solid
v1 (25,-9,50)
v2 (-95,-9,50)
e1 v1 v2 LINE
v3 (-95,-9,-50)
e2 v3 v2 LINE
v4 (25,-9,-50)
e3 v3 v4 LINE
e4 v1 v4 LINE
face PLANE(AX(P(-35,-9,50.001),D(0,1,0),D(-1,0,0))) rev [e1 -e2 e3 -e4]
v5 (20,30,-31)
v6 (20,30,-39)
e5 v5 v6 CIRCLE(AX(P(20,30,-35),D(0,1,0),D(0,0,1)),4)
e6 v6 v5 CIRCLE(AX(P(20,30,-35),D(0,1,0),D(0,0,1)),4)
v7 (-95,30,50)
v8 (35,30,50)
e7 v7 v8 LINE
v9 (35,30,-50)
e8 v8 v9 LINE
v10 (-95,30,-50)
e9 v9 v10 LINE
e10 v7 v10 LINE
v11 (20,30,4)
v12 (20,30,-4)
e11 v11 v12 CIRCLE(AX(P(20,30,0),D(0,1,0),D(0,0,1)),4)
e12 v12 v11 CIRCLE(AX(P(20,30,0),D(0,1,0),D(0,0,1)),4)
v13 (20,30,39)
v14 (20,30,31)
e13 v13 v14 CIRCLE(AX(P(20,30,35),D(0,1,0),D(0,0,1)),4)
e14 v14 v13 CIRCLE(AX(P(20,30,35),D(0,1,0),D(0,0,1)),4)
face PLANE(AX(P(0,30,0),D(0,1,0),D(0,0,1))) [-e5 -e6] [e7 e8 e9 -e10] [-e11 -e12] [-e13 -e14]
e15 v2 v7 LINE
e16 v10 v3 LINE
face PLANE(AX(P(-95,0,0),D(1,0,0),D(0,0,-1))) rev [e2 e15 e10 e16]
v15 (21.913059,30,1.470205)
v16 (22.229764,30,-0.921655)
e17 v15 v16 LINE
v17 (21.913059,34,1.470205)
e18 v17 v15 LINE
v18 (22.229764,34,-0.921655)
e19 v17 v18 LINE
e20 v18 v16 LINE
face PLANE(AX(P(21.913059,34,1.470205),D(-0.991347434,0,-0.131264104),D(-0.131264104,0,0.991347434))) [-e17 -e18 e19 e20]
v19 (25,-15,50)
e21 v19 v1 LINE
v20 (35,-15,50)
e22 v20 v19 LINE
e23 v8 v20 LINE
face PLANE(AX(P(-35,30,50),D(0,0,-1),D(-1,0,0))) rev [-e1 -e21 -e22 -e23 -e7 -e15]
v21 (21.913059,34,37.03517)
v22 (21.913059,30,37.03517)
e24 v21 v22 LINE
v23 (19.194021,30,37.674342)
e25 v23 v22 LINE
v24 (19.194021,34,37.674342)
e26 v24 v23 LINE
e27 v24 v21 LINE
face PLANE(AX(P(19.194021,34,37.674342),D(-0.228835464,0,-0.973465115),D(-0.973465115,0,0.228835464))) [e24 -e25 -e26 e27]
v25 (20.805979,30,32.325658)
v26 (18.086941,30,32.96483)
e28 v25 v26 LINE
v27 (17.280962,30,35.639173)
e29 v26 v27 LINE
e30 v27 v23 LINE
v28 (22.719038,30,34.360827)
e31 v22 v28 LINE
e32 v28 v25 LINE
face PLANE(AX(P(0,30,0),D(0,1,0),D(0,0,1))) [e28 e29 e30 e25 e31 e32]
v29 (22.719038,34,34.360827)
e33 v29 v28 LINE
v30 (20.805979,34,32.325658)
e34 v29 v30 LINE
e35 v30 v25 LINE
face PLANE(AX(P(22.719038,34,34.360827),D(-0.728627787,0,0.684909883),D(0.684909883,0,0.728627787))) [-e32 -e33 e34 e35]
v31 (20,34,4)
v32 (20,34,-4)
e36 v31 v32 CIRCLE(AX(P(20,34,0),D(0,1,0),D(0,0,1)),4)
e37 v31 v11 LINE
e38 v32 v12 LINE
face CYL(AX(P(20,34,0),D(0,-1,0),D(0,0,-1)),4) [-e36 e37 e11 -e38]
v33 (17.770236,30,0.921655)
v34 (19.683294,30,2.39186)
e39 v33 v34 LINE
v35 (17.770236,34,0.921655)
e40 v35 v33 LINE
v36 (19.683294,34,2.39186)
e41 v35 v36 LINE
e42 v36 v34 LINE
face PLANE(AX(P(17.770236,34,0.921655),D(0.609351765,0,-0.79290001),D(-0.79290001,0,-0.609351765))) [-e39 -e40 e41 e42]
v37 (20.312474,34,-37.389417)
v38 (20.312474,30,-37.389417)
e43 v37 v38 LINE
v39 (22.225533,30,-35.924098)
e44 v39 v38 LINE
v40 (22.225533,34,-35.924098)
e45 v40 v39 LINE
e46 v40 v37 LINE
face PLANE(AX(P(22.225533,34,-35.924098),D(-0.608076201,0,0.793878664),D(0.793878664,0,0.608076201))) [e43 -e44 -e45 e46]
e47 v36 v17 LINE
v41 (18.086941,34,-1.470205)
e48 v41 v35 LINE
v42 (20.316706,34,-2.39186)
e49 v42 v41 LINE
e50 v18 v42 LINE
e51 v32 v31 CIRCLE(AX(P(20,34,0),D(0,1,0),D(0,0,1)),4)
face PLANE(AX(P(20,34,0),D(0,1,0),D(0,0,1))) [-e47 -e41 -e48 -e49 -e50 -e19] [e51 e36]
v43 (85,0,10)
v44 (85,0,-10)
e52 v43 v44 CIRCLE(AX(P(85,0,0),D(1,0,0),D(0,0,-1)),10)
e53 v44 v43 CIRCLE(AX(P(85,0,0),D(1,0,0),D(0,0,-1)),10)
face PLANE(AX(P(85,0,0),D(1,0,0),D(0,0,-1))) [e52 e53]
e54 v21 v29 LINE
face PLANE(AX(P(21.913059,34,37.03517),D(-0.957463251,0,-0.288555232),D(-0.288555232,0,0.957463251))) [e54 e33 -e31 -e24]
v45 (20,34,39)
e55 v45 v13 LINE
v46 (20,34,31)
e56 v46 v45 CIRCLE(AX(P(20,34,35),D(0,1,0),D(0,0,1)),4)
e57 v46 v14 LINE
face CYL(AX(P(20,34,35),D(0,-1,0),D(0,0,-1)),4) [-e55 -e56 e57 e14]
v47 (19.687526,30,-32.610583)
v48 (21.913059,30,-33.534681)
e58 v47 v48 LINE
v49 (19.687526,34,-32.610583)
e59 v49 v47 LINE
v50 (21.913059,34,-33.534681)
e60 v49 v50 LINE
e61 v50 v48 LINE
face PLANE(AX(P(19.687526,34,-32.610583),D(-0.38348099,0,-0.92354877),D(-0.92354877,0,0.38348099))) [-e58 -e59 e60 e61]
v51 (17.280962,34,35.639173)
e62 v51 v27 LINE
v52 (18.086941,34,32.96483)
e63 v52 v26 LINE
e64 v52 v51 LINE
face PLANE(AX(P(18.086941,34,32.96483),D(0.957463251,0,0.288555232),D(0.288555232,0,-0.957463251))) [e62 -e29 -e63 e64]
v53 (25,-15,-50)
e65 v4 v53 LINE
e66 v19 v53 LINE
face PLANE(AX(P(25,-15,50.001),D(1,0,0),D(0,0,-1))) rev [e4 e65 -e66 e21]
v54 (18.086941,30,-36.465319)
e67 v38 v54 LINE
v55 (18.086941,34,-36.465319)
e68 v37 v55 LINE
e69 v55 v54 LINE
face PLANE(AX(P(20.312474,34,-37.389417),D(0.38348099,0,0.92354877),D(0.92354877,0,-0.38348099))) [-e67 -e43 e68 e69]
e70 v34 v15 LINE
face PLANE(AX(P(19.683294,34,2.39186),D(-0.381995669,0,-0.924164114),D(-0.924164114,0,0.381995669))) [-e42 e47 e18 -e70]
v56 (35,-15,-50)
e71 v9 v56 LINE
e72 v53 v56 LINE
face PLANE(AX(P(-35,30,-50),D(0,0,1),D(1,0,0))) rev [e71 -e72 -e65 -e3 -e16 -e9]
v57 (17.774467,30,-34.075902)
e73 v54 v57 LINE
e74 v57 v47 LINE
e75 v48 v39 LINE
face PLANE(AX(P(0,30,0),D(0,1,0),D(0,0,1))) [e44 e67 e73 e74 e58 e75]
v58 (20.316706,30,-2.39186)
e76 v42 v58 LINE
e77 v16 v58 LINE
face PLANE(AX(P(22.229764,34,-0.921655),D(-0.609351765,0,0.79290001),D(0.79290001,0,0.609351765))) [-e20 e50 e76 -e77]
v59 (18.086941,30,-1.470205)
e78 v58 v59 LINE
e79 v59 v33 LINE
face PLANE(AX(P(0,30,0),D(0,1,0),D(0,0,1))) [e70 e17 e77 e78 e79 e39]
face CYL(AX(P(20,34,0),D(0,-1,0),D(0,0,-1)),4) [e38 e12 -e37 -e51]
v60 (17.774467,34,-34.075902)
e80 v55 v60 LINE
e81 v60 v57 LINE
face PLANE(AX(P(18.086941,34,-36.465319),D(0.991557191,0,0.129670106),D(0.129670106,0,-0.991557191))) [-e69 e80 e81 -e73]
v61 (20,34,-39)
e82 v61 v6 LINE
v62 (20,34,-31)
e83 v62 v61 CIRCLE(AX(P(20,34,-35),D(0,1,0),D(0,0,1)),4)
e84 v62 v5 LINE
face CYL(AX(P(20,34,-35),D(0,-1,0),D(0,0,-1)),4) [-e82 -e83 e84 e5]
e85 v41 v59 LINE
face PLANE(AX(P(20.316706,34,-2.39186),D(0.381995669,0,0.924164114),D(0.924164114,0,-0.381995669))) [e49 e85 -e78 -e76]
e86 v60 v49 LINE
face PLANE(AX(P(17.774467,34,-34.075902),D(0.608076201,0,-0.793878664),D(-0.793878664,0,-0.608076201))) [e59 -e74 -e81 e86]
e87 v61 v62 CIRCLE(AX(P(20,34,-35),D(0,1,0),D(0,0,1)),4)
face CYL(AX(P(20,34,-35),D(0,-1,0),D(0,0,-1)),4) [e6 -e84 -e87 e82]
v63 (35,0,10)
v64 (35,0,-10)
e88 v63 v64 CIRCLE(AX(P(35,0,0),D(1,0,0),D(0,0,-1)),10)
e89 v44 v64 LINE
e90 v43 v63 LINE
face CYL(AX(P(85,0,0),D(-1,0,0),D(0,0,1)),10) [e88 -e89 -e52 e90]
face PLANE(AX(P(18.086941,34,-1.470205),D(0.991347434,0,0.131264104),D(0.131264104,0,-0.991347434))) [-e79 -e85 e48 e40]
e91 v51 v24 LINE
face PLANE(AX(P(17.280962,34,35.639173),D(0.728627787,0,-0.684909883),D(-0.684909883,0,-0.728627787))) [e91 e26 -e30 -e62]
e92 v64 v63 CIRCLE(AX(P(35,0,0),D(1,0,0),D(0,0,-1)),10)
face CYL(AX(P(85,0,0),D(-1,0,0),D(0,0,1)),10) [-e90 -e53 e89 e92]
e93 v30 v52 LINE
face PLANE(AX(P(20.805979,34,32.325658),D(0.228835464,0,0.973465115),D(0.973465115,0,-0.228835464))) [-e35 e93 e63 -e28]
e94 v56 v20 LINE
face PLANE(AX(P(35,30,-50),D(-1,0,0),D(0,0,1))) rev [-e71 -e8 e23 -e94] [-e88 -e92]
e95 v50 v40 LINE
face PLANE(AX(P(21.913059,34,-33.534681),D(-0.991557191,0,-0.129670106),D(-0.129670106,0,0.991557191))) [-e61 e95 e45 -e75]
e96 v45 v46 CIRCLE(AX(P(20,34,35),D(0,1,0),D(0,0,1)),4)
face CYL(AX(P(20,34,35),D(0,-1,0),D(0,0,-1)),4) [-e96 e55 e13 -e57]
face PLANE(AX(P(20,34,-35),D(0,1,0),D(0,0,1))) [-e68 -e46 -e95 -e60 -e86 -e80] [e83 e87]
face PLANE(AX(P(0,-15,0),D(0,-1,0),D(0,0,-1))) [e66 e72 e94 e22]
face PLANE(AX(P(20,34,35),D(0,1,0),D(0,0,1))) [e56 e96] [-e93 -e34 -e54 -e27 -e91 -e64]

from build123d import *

# Parameters (mm, degrees)
SKETCH1_W           = 70
SKETCH1_H           = 100
BOSS_EXTRUDE1_DEPTH = 30
SKETCH2_R           = 4
BOSS_EXTRUDE2_DEPTH = 4
SKETCH3_R           = 10
BOSS_EXTRUDE3_DEPTH = 50
SKETCH4_W           = 70
SKETCH4_H           = 100
BOSS_EXTRUDE4_DEPTH = 15
CUT_EXTRUDE1_REACH  = 137.577
SKETCH5_W           = 60
SKETCH5_H           = 6
SKETCH6_W           = 100
SKETCH6_H           = 39
BOSS_EXTRUDE5_DEPTH = 60


with BuildPart() as part:
    # Sketch1 → Boss-Extrude1 (new body)
    with BuildSketch(Plane(origin=(0, 0, 0), x_dir=(1, 0, 0), z_dir=(0, 1, 0))):
        Rectangle(SKETCH1_W, SKETCH1_H)
    extrude(amount=BOSS_EXTRUDE1_DEPTH)

    # Sketch2 → Boss-Extrude2 (add)
    # profile 1 of 3: a face of its own
    with BuildSketch(Plane(origin=(0, 30, 0), x_dir=(1, 0, 0), z_dir=(0, 1, 0))):
        with Locations(Location((20, -35, 0), (0, 0, 270))):
            Circle(SKETCH2_R)
        Polygon((21.913058762, -37.035169602), (22.719037957, -34.360827314), (20.805979195, -32.325657712), (18.086941238, -32.964830398), (17.280962043, -35.639172686), (19.194020805, -37.674342288), align=None, mode=Mode.SUBTRACT)
    # profile 2 of 3: a face of its own
    with BuildSketch(Plane(origin=(0, 30, 0), x_dir=(1, 0, 0), z_dir=(0, 1, 0))):
        with Locations(Location((20, 0, 0), (0, 0, 270))):
            Circle(SKETCH2_R)
        Polygon((21.913058762, -1.47020522), (22.229764451, 0.921654877), (20.316705689, 2.391860097), (18.086941238, 1.47020522), (17.770235549, -0.921654877), (19.683294311, -2.391860097), align=None, mode=Mode.SUBTRACT)
    # profile 3 of 3: a face of its own
    with BuildSketch(Plane(origin=(0, 30, 0), x_dir=(1, 0, 0), z_dir=(0, 1, 0))):
        with Locations(Location((20, 35, 0), (0, 0, 270))):
            Circle(SKETCH2_R)
        Polygon((21.913058762, 33.534680981), (22.225532876, 35.924097978), (20.312474114, 37.389416996), (18.086941238, 36.465319019), (17.774467124, 34.075902022), (19.687525886, 32.610583004), align=None, mode=Mode.SUBTRACT)
    extrude(amount=BOSS_EXTRUDE2_DEPTH)

    # Sketch3 → Boss-Extrude3 (add)
    with BuildSketch(Plane(origin=(35, 0, 0), x_dir=(0, 0, -1), z_dir=(1, 0, 0))):
        Circle(SKETCH3_R)
    extrude(amount=BOSS_EXTRUDE3_DEPTH)

    # Sketch4 → Boss-Extrude4 (add)
    with BuildSketch(Plane.XZ):
        Rectangle(SKETCH4_W, SKETCH4_H)
    extrude(amount=BOSS_EXTRUDE4_DEPTH)

    # Sketch5 → Cut-Extrude1 (cut, up to next)
    with BuildSketch(Plane(origin=(0, 0, -50), x_dir=(-1, 0, 0), z_dir=(0, 0, -1)), mode=Mode.PRIVATE) as cut_extrude1_sk1:
        with Locations((5, -12)):
            Rectangle(SKETCH5_W, SKETCH5_H)
    cut_extrude1_tool1 = extrude(cut_extrude1_sk1.sketch, amount=-CUT_EXTRUDE1_REACH, mode=Mode.PRIVATE) & part.part
    add(cut_extrude1_tool1.solids().sort_by_distance((-5, -12, -50))[0], mode=Mode.SUBTRACT)

    # Sketch6 → Boss-Extrude5 (add)
    with BuildSketch(Plane.ZY.offset(35)):
        with Locations((0, 10.5)):
            Rectangle(SKETCH6_W, SKETCH6_H)
    extrude(amount=BOSS_EXTRUDE5_DEPTH)


solid = part.part
